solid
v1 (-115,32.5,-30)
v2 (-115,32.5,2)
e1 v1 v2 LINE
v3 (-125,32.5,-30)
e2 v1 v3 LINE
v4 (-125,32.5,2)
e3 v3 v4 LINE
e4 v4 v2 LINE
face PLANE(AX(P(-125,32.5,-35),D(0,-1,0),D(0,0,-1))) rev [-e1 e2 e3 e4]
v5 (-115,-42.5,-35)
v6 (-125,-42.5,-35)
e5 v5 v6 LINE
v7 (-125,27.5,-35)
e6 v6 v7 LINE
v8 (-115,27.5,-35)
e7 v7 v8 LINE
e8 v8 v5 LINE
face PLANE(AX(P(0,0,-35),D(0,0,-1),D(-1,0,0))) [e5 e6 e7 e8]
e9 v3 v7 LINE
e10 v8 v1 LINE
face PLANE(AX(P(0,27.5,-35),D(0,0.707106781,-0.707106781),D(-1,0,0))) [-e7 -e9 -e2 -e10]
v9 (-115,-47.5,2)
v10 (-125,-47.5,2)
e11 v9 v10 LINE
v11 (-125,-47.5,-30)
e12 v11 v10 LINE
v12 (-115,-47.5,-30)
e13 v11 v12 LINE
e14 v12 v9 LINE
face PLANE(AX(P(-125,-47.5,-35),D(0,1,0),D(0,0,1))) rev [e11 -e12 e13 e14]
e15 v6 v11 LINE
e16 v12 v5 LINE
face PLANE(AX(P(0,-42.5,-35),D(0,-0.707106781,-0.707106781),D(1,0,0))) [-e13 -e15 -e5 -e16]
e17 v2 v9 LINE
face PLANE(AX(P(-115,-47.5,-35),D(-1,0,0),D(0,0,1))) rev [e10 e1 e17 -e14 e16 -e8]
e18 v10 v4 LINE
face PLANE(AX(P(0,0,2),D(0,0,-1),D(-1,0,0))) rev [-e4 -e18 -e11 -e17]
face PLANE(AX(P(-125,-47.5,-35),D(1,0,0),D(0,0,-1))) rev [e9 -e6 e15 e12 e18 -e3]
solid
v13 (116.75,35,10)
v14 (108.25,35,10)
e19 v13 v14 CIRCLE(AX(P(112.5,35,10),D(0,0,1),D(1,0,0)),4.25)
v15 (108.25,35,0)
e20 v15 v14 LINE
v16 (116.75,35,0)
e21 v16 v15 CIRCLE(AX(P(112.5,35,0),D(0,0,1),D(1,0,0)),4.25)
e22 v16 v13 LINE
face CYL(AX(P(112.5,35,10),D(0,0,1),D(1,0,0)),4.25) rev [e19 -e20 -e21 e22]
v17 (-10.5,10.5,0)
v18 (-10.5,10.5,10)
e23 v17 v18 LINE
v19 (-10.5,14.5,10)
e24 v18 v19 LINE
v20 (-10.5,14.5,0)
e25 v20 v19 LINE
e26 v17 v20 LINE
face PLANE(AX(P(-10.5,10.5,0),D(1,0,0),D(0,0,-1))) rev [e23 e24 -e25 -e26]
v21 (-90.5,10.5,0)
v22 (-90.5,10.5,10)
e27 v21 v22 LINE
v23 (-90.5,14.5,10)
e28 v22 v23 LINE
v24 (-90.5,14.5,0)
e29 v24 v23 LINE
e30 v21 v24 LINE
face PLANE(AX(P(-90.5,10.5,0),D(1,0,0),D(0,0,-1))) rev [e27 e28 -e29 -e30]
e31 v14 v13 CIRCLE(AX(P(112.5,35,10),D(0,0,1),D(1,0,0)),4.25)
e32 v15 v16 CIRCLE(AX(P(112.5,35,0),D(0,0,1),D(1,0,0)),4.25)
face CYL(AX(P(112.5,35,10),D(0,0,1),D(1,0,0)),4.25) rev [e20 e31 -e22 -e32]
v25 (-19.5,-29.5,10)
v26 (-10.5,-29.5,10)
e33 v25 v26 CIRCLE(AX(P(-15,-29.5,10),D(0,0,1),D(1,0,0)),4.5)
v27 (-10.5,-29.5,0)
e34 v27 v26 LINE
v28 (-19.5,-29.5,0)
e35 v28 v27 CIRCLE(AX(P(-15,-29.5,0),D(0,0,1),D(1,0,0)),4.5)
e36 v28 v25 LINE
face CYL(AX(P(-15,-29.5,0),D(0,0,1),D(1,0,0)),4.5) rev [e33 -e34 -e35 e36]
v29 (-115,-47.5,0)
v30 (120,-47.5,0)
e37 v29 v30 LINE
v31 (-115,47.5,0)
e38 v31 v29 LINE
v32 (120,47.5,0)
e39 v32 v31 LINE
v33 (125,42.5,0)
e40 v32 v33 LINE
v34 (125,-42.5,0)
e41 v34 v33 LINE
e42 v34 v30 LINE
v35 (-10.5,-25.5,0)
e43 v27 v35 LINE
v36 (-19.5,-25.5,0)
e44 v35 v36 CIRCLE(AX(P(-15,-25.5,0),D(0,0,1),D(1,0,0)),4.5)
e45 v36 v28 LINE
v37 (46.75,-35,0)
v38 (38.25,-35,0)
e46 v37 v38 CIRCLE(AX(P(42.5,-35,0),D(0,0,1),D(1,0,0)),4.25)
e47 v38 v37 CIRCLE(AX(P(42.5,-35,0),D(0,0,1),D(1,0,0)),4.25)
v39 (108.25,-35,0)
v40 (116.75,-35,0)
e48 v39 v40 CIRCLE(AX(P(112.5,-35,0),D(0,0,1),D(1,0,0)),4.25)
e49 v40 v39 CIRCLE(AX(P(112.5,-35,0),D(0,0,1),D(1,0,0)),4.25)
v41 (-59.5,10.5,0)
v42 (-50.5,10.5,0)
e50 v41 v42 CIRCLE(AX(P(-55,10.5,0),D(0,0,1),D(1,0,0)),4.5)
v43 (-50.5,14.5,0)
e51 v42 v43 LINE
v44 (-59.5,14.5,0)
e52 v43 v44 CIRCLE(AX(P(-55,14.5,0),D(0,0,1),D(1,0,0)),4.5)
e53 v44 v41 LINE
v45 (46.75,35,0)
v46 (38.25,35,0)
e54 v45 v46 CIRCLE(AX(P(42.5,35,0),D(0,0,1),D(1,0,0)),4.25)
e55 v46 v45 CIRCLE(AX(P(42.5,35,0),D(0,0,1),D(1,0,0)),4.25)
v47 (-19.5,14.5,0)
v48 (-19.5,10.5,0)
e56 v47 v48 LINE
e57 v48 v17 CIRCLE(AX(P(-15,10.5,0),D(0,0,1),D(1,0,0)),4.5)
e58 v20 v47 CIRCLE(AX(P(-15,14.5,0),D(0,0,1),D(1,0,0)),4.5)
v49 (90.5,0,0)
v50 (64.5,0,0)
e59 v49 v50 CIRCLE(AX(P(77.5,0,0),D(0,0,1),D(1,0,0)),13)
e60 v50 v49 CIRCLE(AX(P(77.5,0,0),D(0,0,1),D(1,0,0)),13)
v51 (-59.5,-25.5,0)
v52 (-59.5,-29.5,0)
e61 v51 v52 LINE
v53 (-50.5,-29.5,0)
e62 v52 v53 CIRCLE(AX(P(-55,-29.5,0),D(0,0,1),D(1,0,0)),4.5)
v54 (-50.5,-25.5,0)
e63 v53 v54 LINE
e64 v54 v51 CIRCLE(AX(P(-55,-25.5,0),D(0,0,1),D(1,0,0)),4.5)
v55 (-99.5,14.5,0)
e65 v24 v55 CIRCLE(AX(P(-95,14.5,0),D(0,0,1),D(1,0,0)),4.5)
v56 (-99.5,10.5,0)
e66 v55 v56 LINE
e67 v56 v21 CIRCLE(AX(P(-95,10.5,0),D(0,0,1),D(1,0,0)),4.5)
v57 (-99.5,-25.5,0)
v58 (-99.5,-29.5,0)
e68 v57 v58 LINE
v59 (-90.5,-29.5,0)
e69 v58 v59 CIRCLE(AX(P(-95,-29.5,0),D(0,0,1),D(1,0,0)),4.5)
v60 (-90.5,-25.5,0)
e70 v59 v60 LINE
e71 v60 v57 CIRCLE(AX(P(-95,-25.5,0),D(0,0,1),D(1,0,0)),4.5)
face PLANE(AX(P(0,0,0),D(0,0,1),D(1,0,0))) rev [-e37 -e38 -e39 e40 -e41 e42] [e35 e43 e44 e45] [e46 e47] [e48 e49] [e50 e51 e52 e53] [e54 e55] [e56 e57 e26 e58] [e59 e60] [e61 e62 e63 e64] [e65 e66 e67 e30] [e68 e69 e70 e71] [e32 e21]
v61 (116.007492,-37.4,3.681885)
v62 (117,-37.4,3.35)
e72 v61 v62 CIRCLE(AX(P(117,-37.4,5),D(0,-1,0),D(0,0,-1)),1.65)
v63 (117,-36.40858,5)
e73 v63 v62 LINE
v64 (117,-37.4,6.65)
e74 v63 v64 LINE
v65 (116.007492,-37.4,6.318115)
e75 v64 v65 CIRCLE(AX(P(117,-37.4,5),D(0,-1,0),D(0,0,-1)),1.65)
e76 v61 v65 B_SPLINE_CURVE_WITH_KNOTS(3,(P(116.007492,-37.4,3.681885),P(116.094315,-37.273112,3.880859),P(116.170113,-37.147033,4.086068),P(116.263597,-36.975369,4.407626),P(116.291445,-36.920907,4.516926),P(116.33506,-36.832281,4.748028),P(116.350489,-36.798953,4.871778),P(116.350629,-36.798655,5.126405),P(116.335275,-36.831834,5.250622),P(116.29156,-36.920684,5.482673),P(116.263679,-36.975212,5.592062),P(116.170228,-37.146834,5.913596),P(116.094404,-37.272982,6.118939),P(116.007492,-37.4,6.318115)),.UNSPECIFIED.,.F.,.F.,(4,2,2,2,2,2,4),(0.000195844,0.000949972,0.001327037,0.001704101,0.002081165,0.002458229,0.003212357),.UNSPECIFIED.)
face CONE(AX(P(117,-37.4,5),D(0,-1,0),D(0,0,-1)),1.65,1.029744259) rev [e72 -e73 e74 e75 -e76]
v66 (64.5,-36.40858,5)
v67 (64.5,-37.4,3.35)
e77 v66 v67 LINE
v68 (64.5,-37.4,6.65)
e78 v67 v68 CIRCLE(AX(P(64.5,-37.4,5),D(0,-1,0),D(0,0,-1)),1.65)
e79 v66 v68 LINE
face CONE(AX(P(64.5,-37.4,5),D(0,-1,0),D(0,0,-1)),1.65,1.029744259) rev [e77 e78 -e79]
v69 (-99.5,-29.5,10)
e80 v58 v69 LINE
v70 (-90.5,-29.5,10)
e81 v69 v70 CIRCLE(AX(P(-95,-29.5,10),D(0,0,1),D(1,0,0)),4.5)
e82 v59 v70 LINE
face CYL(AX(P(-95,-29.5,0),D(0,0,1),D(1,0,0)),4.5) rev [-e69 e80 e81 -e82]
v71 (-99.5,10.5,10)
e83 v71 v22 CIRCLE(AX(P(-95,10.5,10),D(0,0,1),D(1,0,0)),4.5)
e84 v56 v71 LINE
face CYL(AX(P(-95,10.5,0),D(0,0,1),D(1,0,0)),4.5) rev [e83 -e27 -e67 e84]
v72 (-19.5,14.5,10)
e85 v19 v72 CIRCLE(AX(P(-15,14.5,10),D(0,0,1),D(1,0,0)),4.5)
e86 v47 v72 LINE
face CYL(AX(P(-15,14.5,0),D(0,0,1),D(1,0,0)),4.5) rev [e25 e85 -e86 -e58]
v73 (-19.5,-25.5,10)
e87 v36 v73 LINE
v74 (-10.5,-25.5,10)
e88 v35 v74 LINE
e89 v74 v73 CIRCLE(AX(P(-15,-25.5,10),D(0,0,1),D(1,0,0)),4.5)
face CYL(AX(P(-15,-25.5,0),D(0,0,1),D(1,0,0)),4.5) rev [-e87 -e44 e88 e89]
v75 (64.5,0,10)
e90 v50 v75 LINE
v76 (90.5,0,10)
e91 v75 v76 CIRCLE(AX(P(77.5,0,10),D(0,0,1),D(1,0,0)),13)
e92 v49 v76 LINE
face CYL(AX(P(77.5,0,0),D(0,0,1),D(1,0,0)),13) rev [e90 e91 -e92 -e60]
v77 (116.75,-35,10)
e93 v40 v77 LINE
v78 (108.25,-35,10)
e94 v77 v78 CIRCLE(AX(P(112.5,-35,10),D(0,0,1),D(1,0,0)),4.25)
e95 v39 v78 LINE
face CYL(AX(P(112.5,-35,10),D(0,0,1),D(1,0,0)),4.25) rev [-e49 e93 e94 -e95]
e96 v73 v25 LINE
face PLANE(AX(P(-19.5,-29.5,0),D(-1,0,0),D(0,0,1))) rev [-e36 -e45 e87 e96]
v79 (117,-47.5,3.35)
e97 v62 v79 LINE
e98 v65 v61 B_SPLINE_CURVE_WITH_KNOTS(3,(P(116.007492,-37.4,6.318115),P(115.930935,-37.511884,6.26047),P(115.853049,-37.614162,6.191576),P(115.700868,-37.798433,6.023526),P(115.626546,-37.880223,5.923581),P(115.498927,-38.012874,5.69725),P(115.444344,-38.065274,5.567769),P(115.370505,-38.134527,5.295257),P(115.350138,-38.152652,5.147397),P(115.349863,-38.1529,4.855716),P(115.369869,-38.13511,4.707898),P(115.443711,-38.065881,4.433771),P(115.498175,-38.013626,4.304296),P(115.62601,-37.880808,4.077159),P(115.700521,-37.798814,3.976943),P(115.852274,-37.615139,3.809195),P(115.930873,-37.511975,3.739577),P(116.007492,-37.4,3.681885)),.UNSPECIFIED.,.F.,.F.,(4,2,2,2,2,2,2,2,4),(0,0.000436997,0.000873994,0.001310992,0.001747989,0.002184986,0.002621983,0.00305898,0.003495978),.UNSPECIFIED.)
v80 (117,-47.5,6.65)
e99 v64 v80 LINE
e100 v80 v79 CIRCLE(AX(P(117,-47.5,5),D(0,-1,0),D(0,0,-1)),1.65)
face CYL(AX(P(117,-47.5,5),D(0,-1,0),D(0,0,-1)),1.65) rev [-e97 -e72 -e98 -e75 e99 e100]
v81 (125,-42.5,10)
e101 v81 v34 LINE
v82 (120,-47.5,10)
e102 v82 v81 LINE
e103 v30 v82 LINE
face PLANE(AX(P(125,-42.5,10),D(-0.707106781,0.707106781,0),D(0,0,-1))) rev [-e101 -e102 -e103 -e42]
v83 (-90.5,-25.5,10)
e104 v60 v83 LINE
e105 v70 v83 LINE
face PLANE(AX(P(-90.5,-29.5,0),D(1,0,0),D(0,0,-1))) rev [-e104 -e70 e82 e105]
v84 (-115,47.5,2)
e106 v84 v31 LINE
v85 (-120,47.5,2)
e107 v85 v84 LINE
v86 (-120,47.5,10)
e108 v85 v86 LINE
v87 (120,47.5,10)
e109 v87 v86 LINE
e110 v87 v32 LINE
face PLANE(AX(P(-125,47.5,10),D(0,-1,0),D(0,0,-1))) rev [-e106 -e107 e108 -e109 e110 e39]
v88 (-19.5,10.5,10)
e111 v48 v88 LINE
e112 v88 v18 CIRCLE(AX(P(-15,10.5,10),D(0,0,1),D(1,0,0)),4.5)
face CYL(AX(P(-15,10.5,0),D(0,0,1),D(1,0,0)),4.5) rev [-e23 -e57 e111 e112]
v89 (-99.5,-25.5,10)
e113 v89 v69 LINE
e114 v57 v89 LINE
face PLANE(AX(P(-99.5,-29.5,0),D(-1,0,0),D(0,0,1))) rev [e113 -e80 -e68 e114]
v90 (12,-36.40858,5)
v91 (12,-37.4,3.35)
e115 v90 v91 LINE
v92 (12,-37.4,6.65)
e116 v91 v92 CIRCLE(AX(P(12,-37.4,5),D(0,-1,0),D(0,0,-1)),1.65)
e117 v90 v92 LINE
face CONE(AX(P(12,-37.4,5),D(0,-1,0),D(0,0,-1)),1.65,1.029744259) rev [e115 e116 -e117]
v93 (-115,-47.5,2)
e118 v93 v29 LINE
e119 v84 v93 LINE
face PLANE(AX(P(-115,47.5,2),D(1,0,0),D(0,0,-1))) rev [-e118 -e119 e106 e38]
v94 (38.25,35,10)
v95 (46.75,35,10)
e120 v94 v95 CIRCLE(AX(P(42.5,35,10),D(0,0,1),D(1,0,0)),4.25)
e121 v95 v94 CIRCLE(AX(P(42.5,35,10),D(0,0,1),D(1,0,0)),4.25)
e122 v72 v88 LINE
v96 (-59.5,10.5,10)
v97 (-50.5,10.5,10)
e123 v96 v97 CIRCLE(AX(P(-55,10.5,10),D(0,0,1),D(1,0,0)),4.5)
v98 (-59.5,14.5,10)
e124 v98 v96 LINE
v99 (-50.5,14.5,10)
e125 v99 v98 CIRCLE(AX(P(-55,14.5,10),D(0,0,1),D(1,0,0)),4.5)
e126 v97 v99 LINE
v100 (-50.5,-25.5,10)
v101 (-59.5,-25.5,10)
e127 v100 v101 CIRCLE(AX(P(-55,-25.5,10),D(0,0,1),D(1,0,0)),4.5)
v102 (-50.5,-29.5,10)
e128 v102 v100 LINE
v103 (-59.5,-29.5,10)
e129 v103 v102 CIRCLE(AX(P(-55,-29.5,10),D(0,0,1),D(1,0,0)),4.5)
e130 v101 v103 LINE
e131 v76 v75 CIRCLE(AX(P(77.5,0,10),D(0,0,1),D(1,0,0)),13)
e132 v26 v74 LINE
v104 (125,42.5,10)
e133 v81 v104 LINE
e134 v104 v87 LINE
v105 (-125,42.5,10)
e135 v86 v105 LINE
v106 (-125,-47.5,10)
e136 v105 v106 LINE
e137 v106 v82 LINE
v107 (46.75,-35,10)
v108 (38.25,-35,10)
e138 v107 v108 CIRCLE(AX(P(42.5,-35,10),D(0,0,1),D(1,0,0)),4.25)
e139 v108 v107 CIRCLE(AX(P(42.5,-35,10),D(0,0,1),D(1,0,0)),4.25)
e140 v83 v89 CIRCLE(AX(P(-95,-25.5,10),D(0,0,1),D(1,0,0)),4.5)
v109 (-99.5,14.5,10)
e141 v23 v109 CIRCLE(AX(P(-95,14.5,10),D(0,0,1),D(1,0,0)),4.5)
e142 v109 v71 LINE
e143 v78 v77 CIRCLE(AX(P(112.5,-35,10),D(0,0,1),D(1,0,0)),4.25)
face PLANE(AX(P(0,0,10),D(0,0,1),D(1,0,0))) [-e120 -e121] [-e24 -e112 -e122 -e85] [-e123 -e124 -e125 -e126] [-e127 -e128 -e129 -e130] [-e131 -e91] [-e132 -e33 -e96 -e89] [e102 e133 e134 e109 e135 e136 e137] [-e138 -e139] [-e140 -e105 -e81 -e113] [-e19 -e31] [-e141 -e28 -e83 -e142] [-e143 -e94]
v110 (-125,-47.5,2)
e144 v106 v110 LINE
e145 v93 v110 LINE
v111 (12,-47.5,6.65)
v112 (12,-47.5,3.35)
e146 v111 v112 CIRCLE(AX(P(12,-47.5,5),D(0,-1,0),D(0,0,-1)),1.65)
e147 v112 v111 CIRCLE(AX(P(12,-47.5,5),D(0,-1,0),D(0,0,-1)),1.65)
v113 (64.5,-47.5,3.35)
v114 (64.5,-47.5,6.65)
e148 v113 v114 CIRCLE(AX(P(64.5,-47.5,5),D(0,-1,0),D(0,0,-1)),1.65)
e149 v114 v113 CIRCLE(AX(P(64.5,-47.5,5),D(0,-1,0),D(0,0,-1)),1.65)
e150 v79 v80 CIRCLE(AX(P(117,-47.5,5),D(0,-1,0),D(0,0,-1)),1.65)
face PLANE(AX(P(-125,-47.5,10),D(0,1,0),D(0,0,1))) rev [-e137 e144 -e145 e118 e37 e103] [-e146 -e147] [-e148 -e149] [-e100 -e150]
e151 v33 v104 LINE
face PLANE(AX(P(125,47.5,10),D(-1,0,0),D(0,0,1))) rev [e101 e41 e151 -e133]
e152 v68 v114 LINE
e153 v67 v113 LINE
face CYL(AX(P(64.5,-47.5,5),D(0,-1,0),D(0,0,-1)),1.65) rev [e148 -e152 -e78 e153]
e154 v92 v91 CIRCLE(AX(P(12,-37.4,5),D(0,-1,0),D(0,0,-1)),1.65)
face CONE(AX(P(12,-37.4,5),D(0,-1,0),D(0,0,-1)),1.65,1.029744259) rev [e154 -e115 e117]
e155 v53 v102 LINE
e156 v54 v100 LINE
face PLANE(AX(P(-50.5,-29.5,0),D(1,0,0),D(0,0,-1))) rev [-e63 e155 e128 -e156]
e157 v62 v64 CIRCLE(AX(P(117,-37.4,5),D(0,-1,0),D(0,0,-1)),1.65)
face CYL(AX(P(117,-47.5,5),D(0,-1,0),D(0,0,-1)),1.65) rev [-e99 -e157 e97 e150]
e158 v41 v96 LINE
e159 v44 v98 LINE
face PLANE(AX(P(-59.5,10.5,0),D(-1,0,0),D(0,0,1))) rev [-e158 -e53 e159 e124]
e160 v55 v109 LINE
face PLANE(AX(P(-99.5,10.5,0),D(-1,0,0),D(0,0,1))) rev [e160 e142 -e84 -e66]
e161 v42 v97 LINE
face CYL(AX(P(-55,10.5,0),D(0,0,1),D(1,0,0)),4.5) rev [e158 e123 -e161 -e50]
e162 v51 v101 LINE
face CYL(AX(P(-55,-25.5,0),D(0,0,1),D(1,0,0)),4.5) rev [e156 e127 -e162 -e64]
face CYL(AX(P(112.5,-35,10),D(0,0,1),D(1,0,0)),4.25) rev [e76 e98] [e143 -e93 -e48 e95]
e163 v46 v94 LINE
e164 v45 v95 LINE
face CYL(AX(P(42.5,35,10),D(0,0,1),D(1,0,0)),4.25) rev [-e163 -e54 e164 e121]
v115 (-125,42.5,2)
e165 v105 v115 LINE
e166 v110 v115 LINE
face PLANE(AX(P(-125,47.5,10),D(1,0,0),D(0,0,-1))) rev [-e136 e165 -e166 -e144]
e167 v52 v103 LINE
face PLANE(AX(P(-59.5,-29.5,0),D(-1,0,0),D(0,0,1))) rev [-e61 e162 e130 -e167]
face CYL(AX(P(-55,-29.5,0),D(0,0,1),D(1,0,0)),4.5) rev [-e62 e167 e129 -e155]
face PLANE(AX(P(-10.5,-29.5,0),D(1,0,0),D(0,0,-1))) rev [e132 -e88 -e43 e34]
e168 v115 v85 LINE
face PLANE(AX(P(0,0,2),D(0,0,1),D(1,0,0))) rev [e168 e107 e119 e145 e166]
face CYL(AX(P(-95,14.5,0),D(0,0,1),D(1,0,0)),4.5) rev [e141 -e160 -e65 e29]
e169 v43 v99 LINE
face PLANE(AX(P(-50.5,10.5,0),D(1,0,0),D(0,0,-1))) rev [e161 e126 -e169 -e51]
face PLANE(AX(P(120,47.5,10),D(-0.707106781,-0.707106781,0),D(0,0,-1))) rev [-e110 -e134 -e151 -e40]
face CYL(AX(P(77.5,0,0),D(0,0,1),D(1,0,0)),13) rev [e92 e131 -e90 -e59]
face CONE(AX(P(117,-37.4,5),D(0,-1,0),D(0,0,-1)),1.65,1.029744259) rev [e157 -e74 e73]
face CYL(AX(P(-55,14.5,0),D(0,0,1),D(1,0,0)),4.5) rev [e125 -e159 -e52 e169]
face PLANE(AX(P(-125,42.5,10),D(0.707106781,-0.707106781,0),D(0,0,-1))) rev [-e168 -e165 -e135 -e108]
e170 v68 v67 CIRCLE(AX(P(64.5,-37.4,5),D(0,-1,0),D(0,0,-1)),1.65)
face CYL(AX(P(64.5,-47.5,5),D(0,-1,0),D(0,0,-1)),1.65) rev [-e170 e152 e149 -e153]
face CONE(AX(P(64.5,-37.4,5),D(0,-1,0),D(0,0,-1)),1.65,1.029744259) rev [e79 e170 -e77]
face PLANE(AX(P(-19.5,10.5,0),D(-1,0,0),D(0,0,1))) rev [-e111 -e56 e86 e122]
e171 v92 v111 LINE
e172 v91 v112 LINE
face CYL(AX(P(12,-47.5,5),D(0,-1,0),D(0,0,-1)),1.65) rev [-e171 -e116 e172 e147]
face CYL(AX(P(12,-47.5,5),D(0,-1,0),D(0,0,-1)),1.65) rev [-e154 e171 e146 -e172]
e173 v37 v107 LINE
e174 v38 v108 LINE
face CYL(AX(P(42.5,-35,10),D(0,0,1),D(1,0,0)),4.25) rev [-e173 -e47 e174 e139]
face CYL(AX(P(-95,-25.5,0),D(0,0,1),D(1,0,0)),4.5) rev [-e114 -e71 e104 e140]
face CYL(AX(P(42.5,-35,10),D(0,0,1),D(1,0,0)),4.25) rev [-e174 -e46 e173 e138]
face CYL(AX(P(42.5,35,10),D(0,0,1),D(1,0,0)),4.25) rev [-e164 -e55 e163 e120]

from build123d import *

# Parameters (mm, degrees)
SKETCH_1_W                  = 250
SKETCH_1_H                  = 95
EXTRUDE_1_DEPTH             = 10
CUT_EXTRUDE_2_DEPTH         = 135.094183319
PATTERN_LINEAR_1_COUNT      = 2
PATTERN_LINEAR_1_PITCH      = 40
PATTERN_LINEAR_1_COUNT_DIR2 = 2
PATTERN_LINEAR_1_PITCH_DIR2 = 40
PATTERN_LINEAR_2_COUNT      = 2
PATTERN_LINEAR_2_PITCH      = 40
PATTERN_LINEAR_2_COUNT_DIR2 = 2
PATTERN_LINEAR_2_PITCH_DIR2 = 40
HOLE_WIZARD_M10_3_D         = 8.5
HOLE_WIZARD_M10_3_DEPTH     = 24.5
HOLE_WIZARD_M10_3_TIP       = 2.553657631
SKETCH_12_R                 = 13
CUT_EXTRUDE_5_DEPTH         = 135.094183319
HOLE_WIZARD_M4_1_D          = 3.3
HOLE_WIZARD_M4_1_DEPTH      = 10.1
HOLE_WIZARD_M4_1_TIP        = 0.991420021
SKETCH_22_W                 = 10
SKETCH_22_H                 = 95
CUT_EXTRUDE_6_DEPTH         = 2
SKETCH_21_W                 = 10
SKETCH_21_H                 = 80
EXTRUDE_2_DEPTH             = 37
CHAMFER_1_SIZE              = 5
CHAMFER_2_SIZE              = 5


with BuildPart() as part:
    # 草图1 → 凸台-拉伸1 (new body)
    with BuildSketch(Plane.XY):
        Rectangle(SKETCH_1_W, SKETCH_1_H)
    extrude(amount=EXTRUDE_1_DEPTH)

    # 草图3 → 切除-拉伸2 (cut, through all)
    with BuildSketch(Plane.XY.offset(10)):
        with BuildLine():
            Line((-59.5, -29.5), (-59.5, -25.5))
            ThreePointArc((-59.5, -25.5), (-55, -21), (-50.5, -25.5))
            Line((-50.5, -25.5), (-50.5, -29.5))
            ThreePointArc((-50.5, -29.5), (-55, -34), (-59.5, -29.5))
        make_face()
    cut_extrude_2 = extrude(amount=-CUT_EXTRUDE_2_DEPTH, mode=Mode.SUBTRACT)

    # 阵列(线性)1: Cut-Extrude 2 2 × 2
    with Locations(*[(i * PATTERN_LINEAR_1_PITCH, j * PATTERN_LINEAR_1_PITCH_DIR2, 0) for i in range(PATTERN_LINEAR_1_COUNT) for j in range(PATTERN_LINEAR_1_COUNT_DIR2) if (i, j) != (0, 0)]):
        add(cut_extrude_2, mode=Mode.SUBTRACT)

    # 阵列(线性)2: Cut-Extrude 2 2 × 2
    with Locations(*[(-i * PATTERN_LINEAR_2_PITCH, j * PATTERN_LINEAR_2_PITCH_DIR2, 0) for i in range(PATTERN_LINEAR_2_COUNT) for j in range(PATTERN_LINEAR_2_COUNT_DIR2) if (i, j) != (0, 0)]):
        add(cut_extrude_2, mode=Mode.SUBTRACT)

    # M10 螺纹孔3
    with Locations(Plane(origin=(42.5, 35, 10), x_dir=(1, 0, 0), z_dir=(0, 0, 1))):
        with Locations((0, 0), (70, 0), (70, -70), (0, -70)):
            Hole(HOLE_WIZARD_M10_3_D / 2, depth=HOLE_WIZARD_M10_3_DEPTH)
            with Locations((0, 0, -(HOLE_WIZARD_M10_3_DEPTH + HOLE_WIZARD_M10_3_TIP / 2))):  # 118° drill point
                Cone(0, HOLE_WIZARD_M10_3_D / 2, HOLE_WIZARD_M10_3_TIP, mode=Mode.SUBTRACT)

    # 草图12 → 切除-拉伸5 (cut, through all)
    with BuildSketch(Plane.XY.offset(10)):
        with Locations((77.5, 0)):
            Circle(SKETCH_12_R)
    extrude(amount=-CUT_EXTRUDE_5_DEPTH, mode=Mode.SUBTRACT)

    # M4 螺纹孔1
    with Locations(Plane(origin=(117, -47.5, 5), x_dir=(0, 0, -1), z_dir=(0, -1, 0))):
        with Locations((0, 0), (0, -105), (0, -52.5)):
            Hole(HOLE_WIZARD_M4_1_D / 2, depth=HOLE_WIZARD_M4_1_DEPTH)
            with Locations((0, 0, -(HOLE_WIZARD_M4_1_DEPTH + HOLE_WIZARD_M4_1_TIP / 2))):  # 118° drill point
                Cone(0, HOLE_WIZARD_M4_1_D / 2, HOLE_WIZARD_M4_1_TIP, mode=Mode.SUBTRACT)

    # 草图22 → 切除-拉伸6 (cut)
    with BuildSketch(Plane(origin=(0, 0, 0), x_dir=(-1, 0, 0), z_dir=(0, 0, -1))):
        with Locations((120, 0)):
            Rectangle(SKETCH_22_W, SKETCH_22_H)
    extrude(amount=-CUT_EXTRUDE_6_DEPTH, mode=Mode.SUBTRACT)

    # 倒角1
    chamfer_1_edges = [part.edges().sort_by_distance(p)[0] for p in [
        (125, -47.5, 5),
        (-125, 47.5, 6),
        (125, 47.5, 5),
    ]]
    chamfer(chamfer_1_edges, length=CHAMFER_1_SIZE)


with BuildPart() as body_2:
    # 草图21 → 凸台-拉伸2 (new body)
    with BuildSketch(Plane(origin=(0, 0, 2), x_dir=(-1, 0, 0), z_dir=(0, 0, -1))):
        with Locations((120, -7.5)):
            Rectangle(SKETCH_21_W, SKETCH_21_H)
    extrude(amount=EXTRUDE_2_DEPTH)

    # 倒角2
    chamfer_2_edges = [body_2.edges().sort_by_distance(p)[0] for p in [
        (-120, -47.5, -35),
        (-120, 32.5, -35),
    ]]
    chamfer(chamfer_2_edges, length=CHAMFER_2_SIZE)


solid = Compound([part.part, body_2.part])
